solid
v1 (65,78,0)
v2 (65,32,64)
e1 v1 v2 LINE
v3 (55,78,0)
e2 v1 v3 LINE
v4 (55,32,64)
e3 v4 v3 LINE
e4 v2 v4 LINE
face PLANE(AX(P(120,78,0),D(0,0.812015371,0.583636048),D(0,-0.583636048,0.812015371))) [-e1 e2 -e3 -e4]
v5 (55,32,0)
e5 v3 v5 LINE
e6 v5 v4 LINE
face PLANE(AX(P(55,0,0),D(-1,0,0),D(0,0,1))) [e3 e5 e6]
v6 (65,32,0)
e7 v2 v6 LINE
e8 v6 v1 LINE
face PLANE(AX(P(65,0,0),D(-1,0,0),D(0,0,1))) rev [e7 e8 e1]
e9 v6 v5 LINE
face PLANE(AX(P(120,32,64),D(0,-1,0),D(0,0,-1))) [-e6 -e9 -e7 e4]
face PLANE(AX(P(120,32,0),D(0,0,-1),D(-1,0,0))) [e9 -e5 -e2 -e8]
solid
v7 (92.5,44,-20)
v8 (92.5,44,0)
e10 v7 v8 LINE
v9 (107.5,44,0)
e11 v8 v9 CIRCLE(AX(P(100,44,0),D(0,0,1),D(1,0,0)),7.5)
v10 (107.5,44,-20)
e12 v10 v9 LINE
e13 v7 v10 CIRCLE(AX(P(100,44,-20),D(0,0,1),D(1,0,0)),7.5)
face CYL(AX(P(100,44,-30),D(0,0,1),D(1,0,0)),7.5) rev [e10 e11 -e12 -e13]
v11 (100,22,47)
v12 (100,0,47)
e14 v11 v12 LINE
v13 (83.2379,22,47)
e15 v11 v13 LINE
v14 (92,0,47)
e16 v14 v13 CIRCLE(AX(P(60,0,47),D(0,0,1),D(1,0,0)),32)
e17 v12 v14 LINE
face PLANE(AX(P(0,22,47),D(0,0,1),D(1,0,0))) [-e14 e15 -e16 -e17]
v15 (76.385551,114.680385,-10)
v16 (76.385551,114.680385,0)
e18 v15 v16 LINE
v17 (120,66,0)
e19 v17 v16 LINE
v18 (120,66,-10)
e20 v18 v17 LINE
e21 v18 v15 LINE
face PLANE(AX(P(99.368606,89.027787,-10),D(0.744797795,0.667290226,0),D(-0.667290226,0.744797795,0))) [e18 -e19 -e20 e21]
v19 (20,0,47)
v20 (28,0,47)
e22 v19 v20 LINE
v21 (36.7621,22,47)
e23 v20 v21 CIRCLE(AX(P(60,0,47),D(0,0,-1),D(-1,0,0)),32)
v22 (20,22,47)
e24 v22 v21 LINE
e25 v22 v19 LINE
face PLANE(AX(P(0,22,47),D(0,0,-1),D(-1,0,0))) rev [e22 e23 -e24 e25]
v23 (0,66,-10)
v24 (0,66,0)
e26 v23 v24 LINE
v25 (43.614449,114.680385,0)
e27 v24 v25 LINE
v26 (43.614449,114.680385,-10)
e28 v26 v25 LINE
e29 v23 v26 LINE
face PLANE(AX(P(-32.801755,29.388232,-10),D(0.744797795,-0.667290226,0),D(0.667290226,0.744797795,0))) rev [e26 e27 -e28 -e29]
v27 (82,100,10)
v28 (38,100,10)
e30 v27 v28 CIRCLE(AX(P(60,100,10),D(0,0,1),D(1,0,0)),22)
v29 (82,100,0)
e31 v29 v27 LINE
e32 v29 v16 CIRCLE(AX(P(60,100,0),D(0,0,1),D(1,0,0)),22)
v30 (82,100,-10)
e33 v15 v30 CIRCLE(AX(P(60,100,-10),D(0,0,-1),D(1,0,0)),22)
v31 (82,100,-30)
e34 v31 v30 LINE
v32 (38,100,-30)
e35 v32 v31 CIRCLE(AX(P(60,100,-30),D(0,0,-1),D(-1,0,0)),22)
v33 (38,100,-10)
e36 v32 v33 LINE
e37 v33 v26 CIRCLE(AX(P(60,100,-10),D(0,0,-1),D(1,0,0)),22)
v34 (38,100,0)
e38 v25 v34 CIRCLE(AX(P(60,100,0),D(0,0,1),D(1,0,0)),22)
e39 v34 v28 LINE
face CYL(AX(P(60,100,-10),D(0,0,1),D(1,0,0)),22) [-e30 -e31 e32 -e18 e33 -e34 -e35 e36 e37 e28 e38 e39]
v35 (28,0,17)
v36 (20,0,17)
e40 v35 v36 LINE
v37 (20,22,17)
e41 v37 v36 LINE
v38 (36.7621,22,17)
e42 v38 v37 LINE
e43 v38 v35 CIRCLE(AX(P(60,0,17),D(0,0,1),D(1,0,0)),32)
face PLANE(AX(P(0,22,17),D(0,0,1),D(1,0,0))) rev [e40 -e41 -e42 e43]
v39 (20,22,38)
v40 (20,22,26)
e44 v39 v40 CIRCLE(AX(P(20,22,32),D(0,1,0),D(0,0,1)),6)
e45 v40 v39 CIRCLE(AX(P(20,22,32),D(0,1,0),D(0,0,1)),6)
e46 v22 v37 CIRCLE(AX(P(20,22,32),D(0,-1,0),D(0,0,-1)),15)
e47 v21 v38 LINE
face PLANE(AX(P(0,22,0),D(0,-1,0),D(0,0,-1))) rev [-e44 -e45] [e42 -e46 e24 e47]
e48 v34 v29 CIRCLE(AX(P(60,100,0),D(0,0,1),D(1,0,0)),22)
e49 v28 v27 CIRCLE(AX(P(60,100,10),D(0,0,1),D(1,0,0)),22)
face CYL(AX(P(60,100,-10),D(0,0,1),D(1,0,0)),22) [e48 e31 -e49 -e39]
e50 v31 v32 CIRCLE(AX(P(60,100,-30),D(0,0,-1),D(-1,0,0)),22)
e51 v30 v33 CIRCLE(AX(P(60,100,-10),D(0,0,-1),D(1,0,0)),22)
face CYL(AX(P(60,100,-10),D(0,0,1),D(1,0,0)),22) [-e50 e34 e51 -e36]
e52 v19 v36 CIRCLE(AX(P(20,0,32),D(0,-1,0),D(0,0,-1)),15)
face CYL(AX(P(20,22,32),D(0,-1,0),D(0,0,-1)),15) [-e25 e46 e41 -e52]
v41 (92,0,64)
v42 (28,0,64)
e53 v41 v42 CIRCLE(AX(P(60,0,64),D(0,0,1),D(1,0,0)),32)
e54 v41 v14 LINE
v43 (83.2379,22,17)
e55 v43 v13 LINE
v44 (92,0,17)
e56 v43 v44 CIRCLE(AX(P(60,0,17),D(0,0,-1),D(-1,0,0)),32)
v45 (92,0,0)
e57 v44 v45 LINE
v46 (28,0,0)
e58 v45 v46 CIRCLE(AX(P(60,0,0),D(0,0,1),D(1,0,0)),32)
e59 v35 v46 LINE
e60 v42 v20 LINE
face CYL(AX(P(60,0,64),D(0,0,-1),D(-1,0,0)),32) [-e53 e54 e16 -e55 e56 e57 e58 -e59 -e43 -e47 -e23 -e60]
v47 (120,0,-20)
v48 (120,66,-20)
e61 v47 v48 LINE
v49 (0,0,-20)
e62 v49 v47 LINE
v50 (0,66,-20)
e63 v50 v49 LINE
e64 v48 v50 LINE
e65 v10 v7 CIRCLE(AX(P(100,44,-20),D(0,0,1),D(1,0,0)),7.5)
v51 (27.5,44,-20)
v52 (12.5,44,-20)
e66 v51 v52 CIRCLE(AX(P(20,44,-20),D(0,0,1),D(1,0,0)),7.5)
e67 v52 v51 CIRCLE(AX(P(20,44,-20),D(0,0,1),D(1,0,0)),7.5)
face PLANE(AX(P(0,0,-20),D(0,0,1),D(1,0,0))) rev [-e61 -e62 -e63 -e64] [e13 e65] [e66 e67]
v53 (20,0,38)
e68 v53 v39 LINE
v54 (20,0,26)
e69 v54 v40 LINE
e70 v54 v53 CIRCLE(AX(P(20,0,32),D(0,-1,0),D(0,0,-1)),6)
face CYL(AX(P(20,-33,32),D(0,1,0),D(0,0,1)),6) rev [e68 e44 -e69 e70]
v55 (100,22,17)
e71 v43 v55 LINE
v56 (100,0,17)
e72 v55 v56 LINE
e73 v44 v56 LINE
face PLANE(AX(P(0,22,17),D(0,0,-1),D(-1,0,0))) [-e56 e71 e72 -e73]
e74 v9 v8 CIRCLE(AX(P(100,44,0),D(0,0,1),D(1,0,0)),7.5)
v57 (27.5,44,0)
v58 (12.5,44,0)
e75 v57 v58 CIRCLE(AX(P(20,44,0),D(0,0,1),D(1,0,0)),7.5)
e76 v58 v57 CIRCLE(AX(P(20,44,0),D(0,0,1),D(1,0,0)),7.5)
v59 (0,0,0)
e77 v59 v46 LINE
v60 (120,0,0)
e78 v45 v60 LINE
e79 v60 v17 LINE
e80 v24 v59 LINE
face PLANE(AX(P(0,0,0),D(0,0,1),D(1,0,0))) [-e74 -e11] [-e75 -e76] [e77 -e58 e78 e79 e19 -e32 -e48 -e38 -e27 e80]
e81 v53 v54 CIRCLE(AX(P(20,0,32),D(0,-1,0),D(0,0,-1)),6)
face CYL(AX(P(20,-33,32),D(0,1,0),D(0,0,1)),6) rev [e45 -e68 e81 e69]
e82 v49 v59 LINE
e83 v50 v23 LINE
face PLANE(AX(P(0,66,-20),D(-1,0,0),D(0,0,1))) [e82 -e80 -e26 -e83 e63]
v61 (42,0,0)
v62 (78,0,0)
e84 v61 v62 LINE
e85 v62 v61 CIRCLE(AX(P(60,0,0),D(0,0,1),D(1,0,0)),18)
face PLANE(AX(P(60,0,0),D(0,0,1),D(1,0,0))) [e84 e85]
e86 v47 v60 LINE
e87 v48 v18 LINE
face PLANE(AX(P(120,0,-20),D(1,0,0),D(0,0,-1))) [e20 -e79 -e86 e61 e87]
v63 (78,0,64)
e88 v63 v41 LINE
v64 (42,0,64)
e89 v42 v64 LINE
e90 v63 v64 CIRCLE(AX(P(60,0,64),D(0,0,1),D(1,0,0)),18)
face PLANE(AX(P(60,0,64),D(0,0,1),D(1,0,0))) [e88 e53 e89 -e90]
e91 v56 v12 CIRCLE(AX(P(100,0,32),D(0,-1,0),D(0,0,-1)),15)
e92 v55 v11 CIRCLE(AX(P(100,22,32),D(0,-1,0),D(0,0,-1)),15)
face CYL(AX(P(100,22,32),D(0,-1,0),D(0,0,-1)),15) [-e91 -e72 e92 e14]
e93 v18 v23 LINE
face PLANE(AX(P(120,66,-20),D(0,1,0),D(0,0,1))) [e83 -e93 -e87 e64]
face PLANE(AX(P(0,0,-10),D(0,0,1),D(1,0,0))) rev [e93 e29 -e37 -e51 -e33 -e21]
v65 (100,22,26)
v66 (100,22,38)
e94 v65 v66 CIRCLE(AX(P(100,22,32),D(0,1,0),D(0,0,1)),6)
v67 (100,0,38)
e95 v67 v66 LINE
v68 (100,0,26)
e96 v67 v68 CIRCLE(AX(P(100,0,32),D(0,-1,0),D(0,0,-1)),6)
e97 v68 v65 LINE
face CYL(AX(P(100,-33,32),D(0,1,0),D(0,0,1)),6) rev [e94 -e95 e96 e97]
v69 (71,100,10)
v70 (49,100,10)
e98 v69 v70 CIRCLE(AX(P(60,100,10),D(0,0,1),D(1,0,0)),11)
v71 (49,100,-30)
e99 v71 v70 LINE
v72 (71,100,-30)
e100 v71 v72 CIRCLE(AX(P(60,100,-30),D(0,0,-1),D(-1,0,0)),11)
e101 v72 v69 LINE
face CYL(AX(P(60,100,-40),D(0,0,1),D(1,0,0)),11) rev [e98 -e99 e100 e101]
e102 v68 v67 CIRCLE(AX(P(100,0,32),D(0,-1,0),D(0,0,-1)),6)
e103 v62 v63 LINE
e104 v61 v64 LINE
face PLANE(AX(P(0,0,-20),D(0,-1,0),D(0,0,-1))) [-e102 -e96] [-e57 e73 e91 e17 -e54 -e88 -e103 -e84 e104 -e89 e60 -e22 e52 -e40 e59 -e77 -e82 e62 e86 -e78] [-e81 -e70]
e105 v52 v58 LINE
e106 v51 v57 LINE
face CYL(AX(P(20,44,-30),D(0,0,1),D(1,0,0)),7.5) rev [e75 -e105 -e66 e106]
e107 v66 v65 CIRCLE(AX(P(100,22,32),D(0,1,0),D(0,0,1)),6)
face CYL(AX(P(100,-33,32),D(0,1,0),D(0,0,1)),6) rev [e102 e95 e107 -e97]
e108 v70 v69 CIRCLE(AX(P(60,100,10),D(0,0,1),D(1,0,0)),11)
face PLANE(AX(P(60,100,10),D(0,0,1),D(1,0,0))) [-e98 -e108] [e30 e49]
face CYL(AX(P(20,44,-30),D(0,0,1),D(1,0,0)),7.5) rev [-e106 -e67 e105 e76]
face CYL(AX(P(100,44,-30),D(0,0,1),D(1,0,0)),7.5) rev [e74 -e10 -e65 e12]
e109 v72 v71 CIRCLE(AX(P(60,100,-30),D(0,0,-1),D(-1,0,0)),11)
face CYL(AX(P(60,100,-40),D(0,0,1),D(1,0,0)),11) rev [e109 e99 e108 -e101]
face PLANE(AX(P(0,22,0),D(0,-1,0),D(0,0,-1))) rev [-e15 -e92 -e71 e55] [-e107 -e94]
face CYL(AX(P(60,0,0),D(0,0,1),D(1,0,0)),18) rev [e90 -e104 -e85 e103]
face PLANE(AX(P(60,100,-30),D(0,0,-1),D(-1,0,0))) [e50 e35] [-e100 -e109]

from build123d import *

# Parameters (mm, degrees)
BASE_PLATE_SKETCH_W        = 120
BASE_PLATE_SKETCH_H        = 66
BASE_PLATE_DEPTH           = 20
SADDLE_BOSS_R32_DEPTH      = 64
SADDLE_BORE_R18_DEPTH      = 64
UPRIGHT_PLATE_DEPTH        = 10
EYE_START                  = 10
EYE_BOSS_FRONT_SKETCH_R    = 22
EYE_BOSS_FRONT_44_DEPTH    = 10
EYE_BOSS_REAR_SKETCH_R     = 22
EYE_BOSS_REAR_44_DEPTH     = 20
EYE_BORE_SKETCH_R          = 11
EYE_BORE_22_DEPTH          = 50
SADDLE_MOUNTING_LUGS_DEPTH = 22
PLATE_RELIEF_SKETCH_R      = 7.5
PLATE_RELIEF_CUT_DEPTH     = 30
RIB_BLOCK_DEPTH            = 120
RIB_TRIM_SIDE_A_DEPTH      = 55
RIB_TRIM_SIDE_B_DEPTH      = 55
LUG_HOLES_SKETCH_R         = 6
LUG_HOLES_2X_12_DEPTH      = 55


with BuildPart() as part:
    # Base Plate Sketch → Base Plate (new body)
    with BuildSketch(Plane.XY):
        with Locations((60, 33)):
            Rectangle(BASE_PLATE_SKETCH_W, BASE_PLATE_SKETCH_H)
    extrude(amount=-BASE_PLATE_DEPTH)

    # Saddle Boss Sketch → Saddle Boss R32 (add)
    with BuildSketch(Plane.XY):
        with BuildLine():
            Line((28, 0), (92, 0))
            ThreePointArc((92, 0), (60, 32), (28, 0))
        make_face()
    extrude(amount=SADDLE_BOSS_R32_DEPTH)

    # Saddle Bore Sketch → Saddle Bore R18 (cut)
    with BuildSketch(Plane.XY.offset(64)):
        with BuildLine():
            Line((42, 0), (78, 0))
            ThreePointArc((78, 0), (60, 18), (42, 0))
        make_face()
    extrude(amount=-SADDLE_BORE_R18_DEPTH, mode=Mode.SUBTRACT)

    # Upright Plate Sketch → Upright Plate (add)
    with BuildSketch(Plane.XY):
        with BuildLine():
            Line((0, 66), (120, 66))
            Line((120, 66), (76.38555148, 114.680384964))
            ThreePointArc((76.38555148, 114.680384964), (60, 122), (43.61444852, 114.680384964))
            Line((43.61444852, 114.680384964), (0, 66))
        make_face()
    extrude(amount=-UPRIGHT_PLATE_DEPTH)

    # Eye Boss Front Sketch → Eye Boss Front Ø44 (add)
    with BuildSketch(Plane.XY.offset(EYE_START)):
        with Locations((60, 100)):
            Circle(EYE_BOSS_FRONT_SKETCH_R)
    extrude(amount=-EYE_BOSS_FRONT_44_DEPTH)

    # Eye Boss Rear Sketch → Eye Boss Rear Ø44 (add)
    with BuildSketch(Plane(origin=(0, 0, -10), x_dir=(-1, 0, 0), z_dir=(0, 0, -1))):
        with Locations(Location((-60, 100, 0), (0, 0, 180))):
            Circle(EYE_BOSS_REAR_SKETCH_R)
    extrude(amount=EYE_BOSS_REAR_44_DEPTH)

    # Eye Bore Sketch → Eye Bore Ø22 (cut)
    with BuildSketch(Plane.XY.offset(10)):
        with Locations((60, 100)):
            Circle(EYE_BORE_SKETCH_R)
    extrude(amount=-EYE_BORE_22_DEPTH, mode=Mode.SUBTRACT)

    # Mounting Lugs Sketch → Saddle Mounting Lugs (add)
    with BuildSketch(Plane.XZ):
        with BuildLine():
            Line((20, 47), (42, 47))
            Line((42, 47), (42, 17))
            Line((42, 17), (20, 17))
            ThreePointArc((20, 17), (5, 32), (20, 47))
        make_face()
        with BuildLine():
            Line((100, 47), (78, 47))
            Line((78, 47), (78, 17))
            Line((78, 17), (100, 17))
            ThreePointArc((100, 17), (115, 32), (100, 47))
        make_face()
    extrude(amount=-SADDLE_MOUNTING_LUGS_DEPTH)

    # Plate Relief Sketch → Plate Relief Cut (cut)
    with BuildSketch(Plane.XY):
        with Locations((20, 44)):
            Circle(PLATE_RELIEF_SKETCH_R)
        with Locations((100, 44)):
            Circle(PLATE_RELIEF_SKETCH_R)
    extrude(amount=-PLATE_RELIEF_CUT_DEPTH, mode=Mode.SUBTRACT)

    # Lug Holes Sketch → Lug Holes 2xØ12 (cut)
    with BuildSketch(Plane(origin=(0, 22, 0), x_dir=(1, 0, 0), z_dir=(0, 1, 0))):
        with Locations(Location((20, -32, 0), (0, 0, 270))):
            Circle(LUG_HOLES_SKETCH_R)
        with Locations(Location((100, -32, 0), (0, 0, 270))):
            Circle(LUG_HOLES_SKETCH_R)
    extrude(amount=-LUG_HOLES_2X_12_DEPTH, mode=Mode.SUBTRACT)


with BuildPart() as body_2:
    # Rib Block Sketch → Rib Block (new body)
    with BuildSketch(Plane.ZY):
        Polygon((0, 78), (64, 32), (0, 32), align=None)
    extrude(amount=-RIB_BLOCK_DEPTH)

    # Rib Trim Side A Sketch → Rib Trim Side A (cut)
    with BuildSketch(Plane.ZY):
        Polygon((0, 78), (64, 32), (0, 32), align=None)
    extrude(amount=-RIB_TRIM_SIDE_A_DEPTH, mode=Mode.SUBTRACT)

    # Rib Trim Side B Sketch → Rib Trim Side B (cut)
    with BuildSketch(Plane(origin=(120, 0, 0), x_dir=(0, 0, -1), z_dir=(1, 0, 0))):
        Polygon((0, 78), (-64, 32), (0, 32), align=None)
    extrude(amount=-RIB_TRIM_SIDE_B_DEPTH, mode=Mode.SUBTRACT)


solid = Compound([part.part, body_2.part])
